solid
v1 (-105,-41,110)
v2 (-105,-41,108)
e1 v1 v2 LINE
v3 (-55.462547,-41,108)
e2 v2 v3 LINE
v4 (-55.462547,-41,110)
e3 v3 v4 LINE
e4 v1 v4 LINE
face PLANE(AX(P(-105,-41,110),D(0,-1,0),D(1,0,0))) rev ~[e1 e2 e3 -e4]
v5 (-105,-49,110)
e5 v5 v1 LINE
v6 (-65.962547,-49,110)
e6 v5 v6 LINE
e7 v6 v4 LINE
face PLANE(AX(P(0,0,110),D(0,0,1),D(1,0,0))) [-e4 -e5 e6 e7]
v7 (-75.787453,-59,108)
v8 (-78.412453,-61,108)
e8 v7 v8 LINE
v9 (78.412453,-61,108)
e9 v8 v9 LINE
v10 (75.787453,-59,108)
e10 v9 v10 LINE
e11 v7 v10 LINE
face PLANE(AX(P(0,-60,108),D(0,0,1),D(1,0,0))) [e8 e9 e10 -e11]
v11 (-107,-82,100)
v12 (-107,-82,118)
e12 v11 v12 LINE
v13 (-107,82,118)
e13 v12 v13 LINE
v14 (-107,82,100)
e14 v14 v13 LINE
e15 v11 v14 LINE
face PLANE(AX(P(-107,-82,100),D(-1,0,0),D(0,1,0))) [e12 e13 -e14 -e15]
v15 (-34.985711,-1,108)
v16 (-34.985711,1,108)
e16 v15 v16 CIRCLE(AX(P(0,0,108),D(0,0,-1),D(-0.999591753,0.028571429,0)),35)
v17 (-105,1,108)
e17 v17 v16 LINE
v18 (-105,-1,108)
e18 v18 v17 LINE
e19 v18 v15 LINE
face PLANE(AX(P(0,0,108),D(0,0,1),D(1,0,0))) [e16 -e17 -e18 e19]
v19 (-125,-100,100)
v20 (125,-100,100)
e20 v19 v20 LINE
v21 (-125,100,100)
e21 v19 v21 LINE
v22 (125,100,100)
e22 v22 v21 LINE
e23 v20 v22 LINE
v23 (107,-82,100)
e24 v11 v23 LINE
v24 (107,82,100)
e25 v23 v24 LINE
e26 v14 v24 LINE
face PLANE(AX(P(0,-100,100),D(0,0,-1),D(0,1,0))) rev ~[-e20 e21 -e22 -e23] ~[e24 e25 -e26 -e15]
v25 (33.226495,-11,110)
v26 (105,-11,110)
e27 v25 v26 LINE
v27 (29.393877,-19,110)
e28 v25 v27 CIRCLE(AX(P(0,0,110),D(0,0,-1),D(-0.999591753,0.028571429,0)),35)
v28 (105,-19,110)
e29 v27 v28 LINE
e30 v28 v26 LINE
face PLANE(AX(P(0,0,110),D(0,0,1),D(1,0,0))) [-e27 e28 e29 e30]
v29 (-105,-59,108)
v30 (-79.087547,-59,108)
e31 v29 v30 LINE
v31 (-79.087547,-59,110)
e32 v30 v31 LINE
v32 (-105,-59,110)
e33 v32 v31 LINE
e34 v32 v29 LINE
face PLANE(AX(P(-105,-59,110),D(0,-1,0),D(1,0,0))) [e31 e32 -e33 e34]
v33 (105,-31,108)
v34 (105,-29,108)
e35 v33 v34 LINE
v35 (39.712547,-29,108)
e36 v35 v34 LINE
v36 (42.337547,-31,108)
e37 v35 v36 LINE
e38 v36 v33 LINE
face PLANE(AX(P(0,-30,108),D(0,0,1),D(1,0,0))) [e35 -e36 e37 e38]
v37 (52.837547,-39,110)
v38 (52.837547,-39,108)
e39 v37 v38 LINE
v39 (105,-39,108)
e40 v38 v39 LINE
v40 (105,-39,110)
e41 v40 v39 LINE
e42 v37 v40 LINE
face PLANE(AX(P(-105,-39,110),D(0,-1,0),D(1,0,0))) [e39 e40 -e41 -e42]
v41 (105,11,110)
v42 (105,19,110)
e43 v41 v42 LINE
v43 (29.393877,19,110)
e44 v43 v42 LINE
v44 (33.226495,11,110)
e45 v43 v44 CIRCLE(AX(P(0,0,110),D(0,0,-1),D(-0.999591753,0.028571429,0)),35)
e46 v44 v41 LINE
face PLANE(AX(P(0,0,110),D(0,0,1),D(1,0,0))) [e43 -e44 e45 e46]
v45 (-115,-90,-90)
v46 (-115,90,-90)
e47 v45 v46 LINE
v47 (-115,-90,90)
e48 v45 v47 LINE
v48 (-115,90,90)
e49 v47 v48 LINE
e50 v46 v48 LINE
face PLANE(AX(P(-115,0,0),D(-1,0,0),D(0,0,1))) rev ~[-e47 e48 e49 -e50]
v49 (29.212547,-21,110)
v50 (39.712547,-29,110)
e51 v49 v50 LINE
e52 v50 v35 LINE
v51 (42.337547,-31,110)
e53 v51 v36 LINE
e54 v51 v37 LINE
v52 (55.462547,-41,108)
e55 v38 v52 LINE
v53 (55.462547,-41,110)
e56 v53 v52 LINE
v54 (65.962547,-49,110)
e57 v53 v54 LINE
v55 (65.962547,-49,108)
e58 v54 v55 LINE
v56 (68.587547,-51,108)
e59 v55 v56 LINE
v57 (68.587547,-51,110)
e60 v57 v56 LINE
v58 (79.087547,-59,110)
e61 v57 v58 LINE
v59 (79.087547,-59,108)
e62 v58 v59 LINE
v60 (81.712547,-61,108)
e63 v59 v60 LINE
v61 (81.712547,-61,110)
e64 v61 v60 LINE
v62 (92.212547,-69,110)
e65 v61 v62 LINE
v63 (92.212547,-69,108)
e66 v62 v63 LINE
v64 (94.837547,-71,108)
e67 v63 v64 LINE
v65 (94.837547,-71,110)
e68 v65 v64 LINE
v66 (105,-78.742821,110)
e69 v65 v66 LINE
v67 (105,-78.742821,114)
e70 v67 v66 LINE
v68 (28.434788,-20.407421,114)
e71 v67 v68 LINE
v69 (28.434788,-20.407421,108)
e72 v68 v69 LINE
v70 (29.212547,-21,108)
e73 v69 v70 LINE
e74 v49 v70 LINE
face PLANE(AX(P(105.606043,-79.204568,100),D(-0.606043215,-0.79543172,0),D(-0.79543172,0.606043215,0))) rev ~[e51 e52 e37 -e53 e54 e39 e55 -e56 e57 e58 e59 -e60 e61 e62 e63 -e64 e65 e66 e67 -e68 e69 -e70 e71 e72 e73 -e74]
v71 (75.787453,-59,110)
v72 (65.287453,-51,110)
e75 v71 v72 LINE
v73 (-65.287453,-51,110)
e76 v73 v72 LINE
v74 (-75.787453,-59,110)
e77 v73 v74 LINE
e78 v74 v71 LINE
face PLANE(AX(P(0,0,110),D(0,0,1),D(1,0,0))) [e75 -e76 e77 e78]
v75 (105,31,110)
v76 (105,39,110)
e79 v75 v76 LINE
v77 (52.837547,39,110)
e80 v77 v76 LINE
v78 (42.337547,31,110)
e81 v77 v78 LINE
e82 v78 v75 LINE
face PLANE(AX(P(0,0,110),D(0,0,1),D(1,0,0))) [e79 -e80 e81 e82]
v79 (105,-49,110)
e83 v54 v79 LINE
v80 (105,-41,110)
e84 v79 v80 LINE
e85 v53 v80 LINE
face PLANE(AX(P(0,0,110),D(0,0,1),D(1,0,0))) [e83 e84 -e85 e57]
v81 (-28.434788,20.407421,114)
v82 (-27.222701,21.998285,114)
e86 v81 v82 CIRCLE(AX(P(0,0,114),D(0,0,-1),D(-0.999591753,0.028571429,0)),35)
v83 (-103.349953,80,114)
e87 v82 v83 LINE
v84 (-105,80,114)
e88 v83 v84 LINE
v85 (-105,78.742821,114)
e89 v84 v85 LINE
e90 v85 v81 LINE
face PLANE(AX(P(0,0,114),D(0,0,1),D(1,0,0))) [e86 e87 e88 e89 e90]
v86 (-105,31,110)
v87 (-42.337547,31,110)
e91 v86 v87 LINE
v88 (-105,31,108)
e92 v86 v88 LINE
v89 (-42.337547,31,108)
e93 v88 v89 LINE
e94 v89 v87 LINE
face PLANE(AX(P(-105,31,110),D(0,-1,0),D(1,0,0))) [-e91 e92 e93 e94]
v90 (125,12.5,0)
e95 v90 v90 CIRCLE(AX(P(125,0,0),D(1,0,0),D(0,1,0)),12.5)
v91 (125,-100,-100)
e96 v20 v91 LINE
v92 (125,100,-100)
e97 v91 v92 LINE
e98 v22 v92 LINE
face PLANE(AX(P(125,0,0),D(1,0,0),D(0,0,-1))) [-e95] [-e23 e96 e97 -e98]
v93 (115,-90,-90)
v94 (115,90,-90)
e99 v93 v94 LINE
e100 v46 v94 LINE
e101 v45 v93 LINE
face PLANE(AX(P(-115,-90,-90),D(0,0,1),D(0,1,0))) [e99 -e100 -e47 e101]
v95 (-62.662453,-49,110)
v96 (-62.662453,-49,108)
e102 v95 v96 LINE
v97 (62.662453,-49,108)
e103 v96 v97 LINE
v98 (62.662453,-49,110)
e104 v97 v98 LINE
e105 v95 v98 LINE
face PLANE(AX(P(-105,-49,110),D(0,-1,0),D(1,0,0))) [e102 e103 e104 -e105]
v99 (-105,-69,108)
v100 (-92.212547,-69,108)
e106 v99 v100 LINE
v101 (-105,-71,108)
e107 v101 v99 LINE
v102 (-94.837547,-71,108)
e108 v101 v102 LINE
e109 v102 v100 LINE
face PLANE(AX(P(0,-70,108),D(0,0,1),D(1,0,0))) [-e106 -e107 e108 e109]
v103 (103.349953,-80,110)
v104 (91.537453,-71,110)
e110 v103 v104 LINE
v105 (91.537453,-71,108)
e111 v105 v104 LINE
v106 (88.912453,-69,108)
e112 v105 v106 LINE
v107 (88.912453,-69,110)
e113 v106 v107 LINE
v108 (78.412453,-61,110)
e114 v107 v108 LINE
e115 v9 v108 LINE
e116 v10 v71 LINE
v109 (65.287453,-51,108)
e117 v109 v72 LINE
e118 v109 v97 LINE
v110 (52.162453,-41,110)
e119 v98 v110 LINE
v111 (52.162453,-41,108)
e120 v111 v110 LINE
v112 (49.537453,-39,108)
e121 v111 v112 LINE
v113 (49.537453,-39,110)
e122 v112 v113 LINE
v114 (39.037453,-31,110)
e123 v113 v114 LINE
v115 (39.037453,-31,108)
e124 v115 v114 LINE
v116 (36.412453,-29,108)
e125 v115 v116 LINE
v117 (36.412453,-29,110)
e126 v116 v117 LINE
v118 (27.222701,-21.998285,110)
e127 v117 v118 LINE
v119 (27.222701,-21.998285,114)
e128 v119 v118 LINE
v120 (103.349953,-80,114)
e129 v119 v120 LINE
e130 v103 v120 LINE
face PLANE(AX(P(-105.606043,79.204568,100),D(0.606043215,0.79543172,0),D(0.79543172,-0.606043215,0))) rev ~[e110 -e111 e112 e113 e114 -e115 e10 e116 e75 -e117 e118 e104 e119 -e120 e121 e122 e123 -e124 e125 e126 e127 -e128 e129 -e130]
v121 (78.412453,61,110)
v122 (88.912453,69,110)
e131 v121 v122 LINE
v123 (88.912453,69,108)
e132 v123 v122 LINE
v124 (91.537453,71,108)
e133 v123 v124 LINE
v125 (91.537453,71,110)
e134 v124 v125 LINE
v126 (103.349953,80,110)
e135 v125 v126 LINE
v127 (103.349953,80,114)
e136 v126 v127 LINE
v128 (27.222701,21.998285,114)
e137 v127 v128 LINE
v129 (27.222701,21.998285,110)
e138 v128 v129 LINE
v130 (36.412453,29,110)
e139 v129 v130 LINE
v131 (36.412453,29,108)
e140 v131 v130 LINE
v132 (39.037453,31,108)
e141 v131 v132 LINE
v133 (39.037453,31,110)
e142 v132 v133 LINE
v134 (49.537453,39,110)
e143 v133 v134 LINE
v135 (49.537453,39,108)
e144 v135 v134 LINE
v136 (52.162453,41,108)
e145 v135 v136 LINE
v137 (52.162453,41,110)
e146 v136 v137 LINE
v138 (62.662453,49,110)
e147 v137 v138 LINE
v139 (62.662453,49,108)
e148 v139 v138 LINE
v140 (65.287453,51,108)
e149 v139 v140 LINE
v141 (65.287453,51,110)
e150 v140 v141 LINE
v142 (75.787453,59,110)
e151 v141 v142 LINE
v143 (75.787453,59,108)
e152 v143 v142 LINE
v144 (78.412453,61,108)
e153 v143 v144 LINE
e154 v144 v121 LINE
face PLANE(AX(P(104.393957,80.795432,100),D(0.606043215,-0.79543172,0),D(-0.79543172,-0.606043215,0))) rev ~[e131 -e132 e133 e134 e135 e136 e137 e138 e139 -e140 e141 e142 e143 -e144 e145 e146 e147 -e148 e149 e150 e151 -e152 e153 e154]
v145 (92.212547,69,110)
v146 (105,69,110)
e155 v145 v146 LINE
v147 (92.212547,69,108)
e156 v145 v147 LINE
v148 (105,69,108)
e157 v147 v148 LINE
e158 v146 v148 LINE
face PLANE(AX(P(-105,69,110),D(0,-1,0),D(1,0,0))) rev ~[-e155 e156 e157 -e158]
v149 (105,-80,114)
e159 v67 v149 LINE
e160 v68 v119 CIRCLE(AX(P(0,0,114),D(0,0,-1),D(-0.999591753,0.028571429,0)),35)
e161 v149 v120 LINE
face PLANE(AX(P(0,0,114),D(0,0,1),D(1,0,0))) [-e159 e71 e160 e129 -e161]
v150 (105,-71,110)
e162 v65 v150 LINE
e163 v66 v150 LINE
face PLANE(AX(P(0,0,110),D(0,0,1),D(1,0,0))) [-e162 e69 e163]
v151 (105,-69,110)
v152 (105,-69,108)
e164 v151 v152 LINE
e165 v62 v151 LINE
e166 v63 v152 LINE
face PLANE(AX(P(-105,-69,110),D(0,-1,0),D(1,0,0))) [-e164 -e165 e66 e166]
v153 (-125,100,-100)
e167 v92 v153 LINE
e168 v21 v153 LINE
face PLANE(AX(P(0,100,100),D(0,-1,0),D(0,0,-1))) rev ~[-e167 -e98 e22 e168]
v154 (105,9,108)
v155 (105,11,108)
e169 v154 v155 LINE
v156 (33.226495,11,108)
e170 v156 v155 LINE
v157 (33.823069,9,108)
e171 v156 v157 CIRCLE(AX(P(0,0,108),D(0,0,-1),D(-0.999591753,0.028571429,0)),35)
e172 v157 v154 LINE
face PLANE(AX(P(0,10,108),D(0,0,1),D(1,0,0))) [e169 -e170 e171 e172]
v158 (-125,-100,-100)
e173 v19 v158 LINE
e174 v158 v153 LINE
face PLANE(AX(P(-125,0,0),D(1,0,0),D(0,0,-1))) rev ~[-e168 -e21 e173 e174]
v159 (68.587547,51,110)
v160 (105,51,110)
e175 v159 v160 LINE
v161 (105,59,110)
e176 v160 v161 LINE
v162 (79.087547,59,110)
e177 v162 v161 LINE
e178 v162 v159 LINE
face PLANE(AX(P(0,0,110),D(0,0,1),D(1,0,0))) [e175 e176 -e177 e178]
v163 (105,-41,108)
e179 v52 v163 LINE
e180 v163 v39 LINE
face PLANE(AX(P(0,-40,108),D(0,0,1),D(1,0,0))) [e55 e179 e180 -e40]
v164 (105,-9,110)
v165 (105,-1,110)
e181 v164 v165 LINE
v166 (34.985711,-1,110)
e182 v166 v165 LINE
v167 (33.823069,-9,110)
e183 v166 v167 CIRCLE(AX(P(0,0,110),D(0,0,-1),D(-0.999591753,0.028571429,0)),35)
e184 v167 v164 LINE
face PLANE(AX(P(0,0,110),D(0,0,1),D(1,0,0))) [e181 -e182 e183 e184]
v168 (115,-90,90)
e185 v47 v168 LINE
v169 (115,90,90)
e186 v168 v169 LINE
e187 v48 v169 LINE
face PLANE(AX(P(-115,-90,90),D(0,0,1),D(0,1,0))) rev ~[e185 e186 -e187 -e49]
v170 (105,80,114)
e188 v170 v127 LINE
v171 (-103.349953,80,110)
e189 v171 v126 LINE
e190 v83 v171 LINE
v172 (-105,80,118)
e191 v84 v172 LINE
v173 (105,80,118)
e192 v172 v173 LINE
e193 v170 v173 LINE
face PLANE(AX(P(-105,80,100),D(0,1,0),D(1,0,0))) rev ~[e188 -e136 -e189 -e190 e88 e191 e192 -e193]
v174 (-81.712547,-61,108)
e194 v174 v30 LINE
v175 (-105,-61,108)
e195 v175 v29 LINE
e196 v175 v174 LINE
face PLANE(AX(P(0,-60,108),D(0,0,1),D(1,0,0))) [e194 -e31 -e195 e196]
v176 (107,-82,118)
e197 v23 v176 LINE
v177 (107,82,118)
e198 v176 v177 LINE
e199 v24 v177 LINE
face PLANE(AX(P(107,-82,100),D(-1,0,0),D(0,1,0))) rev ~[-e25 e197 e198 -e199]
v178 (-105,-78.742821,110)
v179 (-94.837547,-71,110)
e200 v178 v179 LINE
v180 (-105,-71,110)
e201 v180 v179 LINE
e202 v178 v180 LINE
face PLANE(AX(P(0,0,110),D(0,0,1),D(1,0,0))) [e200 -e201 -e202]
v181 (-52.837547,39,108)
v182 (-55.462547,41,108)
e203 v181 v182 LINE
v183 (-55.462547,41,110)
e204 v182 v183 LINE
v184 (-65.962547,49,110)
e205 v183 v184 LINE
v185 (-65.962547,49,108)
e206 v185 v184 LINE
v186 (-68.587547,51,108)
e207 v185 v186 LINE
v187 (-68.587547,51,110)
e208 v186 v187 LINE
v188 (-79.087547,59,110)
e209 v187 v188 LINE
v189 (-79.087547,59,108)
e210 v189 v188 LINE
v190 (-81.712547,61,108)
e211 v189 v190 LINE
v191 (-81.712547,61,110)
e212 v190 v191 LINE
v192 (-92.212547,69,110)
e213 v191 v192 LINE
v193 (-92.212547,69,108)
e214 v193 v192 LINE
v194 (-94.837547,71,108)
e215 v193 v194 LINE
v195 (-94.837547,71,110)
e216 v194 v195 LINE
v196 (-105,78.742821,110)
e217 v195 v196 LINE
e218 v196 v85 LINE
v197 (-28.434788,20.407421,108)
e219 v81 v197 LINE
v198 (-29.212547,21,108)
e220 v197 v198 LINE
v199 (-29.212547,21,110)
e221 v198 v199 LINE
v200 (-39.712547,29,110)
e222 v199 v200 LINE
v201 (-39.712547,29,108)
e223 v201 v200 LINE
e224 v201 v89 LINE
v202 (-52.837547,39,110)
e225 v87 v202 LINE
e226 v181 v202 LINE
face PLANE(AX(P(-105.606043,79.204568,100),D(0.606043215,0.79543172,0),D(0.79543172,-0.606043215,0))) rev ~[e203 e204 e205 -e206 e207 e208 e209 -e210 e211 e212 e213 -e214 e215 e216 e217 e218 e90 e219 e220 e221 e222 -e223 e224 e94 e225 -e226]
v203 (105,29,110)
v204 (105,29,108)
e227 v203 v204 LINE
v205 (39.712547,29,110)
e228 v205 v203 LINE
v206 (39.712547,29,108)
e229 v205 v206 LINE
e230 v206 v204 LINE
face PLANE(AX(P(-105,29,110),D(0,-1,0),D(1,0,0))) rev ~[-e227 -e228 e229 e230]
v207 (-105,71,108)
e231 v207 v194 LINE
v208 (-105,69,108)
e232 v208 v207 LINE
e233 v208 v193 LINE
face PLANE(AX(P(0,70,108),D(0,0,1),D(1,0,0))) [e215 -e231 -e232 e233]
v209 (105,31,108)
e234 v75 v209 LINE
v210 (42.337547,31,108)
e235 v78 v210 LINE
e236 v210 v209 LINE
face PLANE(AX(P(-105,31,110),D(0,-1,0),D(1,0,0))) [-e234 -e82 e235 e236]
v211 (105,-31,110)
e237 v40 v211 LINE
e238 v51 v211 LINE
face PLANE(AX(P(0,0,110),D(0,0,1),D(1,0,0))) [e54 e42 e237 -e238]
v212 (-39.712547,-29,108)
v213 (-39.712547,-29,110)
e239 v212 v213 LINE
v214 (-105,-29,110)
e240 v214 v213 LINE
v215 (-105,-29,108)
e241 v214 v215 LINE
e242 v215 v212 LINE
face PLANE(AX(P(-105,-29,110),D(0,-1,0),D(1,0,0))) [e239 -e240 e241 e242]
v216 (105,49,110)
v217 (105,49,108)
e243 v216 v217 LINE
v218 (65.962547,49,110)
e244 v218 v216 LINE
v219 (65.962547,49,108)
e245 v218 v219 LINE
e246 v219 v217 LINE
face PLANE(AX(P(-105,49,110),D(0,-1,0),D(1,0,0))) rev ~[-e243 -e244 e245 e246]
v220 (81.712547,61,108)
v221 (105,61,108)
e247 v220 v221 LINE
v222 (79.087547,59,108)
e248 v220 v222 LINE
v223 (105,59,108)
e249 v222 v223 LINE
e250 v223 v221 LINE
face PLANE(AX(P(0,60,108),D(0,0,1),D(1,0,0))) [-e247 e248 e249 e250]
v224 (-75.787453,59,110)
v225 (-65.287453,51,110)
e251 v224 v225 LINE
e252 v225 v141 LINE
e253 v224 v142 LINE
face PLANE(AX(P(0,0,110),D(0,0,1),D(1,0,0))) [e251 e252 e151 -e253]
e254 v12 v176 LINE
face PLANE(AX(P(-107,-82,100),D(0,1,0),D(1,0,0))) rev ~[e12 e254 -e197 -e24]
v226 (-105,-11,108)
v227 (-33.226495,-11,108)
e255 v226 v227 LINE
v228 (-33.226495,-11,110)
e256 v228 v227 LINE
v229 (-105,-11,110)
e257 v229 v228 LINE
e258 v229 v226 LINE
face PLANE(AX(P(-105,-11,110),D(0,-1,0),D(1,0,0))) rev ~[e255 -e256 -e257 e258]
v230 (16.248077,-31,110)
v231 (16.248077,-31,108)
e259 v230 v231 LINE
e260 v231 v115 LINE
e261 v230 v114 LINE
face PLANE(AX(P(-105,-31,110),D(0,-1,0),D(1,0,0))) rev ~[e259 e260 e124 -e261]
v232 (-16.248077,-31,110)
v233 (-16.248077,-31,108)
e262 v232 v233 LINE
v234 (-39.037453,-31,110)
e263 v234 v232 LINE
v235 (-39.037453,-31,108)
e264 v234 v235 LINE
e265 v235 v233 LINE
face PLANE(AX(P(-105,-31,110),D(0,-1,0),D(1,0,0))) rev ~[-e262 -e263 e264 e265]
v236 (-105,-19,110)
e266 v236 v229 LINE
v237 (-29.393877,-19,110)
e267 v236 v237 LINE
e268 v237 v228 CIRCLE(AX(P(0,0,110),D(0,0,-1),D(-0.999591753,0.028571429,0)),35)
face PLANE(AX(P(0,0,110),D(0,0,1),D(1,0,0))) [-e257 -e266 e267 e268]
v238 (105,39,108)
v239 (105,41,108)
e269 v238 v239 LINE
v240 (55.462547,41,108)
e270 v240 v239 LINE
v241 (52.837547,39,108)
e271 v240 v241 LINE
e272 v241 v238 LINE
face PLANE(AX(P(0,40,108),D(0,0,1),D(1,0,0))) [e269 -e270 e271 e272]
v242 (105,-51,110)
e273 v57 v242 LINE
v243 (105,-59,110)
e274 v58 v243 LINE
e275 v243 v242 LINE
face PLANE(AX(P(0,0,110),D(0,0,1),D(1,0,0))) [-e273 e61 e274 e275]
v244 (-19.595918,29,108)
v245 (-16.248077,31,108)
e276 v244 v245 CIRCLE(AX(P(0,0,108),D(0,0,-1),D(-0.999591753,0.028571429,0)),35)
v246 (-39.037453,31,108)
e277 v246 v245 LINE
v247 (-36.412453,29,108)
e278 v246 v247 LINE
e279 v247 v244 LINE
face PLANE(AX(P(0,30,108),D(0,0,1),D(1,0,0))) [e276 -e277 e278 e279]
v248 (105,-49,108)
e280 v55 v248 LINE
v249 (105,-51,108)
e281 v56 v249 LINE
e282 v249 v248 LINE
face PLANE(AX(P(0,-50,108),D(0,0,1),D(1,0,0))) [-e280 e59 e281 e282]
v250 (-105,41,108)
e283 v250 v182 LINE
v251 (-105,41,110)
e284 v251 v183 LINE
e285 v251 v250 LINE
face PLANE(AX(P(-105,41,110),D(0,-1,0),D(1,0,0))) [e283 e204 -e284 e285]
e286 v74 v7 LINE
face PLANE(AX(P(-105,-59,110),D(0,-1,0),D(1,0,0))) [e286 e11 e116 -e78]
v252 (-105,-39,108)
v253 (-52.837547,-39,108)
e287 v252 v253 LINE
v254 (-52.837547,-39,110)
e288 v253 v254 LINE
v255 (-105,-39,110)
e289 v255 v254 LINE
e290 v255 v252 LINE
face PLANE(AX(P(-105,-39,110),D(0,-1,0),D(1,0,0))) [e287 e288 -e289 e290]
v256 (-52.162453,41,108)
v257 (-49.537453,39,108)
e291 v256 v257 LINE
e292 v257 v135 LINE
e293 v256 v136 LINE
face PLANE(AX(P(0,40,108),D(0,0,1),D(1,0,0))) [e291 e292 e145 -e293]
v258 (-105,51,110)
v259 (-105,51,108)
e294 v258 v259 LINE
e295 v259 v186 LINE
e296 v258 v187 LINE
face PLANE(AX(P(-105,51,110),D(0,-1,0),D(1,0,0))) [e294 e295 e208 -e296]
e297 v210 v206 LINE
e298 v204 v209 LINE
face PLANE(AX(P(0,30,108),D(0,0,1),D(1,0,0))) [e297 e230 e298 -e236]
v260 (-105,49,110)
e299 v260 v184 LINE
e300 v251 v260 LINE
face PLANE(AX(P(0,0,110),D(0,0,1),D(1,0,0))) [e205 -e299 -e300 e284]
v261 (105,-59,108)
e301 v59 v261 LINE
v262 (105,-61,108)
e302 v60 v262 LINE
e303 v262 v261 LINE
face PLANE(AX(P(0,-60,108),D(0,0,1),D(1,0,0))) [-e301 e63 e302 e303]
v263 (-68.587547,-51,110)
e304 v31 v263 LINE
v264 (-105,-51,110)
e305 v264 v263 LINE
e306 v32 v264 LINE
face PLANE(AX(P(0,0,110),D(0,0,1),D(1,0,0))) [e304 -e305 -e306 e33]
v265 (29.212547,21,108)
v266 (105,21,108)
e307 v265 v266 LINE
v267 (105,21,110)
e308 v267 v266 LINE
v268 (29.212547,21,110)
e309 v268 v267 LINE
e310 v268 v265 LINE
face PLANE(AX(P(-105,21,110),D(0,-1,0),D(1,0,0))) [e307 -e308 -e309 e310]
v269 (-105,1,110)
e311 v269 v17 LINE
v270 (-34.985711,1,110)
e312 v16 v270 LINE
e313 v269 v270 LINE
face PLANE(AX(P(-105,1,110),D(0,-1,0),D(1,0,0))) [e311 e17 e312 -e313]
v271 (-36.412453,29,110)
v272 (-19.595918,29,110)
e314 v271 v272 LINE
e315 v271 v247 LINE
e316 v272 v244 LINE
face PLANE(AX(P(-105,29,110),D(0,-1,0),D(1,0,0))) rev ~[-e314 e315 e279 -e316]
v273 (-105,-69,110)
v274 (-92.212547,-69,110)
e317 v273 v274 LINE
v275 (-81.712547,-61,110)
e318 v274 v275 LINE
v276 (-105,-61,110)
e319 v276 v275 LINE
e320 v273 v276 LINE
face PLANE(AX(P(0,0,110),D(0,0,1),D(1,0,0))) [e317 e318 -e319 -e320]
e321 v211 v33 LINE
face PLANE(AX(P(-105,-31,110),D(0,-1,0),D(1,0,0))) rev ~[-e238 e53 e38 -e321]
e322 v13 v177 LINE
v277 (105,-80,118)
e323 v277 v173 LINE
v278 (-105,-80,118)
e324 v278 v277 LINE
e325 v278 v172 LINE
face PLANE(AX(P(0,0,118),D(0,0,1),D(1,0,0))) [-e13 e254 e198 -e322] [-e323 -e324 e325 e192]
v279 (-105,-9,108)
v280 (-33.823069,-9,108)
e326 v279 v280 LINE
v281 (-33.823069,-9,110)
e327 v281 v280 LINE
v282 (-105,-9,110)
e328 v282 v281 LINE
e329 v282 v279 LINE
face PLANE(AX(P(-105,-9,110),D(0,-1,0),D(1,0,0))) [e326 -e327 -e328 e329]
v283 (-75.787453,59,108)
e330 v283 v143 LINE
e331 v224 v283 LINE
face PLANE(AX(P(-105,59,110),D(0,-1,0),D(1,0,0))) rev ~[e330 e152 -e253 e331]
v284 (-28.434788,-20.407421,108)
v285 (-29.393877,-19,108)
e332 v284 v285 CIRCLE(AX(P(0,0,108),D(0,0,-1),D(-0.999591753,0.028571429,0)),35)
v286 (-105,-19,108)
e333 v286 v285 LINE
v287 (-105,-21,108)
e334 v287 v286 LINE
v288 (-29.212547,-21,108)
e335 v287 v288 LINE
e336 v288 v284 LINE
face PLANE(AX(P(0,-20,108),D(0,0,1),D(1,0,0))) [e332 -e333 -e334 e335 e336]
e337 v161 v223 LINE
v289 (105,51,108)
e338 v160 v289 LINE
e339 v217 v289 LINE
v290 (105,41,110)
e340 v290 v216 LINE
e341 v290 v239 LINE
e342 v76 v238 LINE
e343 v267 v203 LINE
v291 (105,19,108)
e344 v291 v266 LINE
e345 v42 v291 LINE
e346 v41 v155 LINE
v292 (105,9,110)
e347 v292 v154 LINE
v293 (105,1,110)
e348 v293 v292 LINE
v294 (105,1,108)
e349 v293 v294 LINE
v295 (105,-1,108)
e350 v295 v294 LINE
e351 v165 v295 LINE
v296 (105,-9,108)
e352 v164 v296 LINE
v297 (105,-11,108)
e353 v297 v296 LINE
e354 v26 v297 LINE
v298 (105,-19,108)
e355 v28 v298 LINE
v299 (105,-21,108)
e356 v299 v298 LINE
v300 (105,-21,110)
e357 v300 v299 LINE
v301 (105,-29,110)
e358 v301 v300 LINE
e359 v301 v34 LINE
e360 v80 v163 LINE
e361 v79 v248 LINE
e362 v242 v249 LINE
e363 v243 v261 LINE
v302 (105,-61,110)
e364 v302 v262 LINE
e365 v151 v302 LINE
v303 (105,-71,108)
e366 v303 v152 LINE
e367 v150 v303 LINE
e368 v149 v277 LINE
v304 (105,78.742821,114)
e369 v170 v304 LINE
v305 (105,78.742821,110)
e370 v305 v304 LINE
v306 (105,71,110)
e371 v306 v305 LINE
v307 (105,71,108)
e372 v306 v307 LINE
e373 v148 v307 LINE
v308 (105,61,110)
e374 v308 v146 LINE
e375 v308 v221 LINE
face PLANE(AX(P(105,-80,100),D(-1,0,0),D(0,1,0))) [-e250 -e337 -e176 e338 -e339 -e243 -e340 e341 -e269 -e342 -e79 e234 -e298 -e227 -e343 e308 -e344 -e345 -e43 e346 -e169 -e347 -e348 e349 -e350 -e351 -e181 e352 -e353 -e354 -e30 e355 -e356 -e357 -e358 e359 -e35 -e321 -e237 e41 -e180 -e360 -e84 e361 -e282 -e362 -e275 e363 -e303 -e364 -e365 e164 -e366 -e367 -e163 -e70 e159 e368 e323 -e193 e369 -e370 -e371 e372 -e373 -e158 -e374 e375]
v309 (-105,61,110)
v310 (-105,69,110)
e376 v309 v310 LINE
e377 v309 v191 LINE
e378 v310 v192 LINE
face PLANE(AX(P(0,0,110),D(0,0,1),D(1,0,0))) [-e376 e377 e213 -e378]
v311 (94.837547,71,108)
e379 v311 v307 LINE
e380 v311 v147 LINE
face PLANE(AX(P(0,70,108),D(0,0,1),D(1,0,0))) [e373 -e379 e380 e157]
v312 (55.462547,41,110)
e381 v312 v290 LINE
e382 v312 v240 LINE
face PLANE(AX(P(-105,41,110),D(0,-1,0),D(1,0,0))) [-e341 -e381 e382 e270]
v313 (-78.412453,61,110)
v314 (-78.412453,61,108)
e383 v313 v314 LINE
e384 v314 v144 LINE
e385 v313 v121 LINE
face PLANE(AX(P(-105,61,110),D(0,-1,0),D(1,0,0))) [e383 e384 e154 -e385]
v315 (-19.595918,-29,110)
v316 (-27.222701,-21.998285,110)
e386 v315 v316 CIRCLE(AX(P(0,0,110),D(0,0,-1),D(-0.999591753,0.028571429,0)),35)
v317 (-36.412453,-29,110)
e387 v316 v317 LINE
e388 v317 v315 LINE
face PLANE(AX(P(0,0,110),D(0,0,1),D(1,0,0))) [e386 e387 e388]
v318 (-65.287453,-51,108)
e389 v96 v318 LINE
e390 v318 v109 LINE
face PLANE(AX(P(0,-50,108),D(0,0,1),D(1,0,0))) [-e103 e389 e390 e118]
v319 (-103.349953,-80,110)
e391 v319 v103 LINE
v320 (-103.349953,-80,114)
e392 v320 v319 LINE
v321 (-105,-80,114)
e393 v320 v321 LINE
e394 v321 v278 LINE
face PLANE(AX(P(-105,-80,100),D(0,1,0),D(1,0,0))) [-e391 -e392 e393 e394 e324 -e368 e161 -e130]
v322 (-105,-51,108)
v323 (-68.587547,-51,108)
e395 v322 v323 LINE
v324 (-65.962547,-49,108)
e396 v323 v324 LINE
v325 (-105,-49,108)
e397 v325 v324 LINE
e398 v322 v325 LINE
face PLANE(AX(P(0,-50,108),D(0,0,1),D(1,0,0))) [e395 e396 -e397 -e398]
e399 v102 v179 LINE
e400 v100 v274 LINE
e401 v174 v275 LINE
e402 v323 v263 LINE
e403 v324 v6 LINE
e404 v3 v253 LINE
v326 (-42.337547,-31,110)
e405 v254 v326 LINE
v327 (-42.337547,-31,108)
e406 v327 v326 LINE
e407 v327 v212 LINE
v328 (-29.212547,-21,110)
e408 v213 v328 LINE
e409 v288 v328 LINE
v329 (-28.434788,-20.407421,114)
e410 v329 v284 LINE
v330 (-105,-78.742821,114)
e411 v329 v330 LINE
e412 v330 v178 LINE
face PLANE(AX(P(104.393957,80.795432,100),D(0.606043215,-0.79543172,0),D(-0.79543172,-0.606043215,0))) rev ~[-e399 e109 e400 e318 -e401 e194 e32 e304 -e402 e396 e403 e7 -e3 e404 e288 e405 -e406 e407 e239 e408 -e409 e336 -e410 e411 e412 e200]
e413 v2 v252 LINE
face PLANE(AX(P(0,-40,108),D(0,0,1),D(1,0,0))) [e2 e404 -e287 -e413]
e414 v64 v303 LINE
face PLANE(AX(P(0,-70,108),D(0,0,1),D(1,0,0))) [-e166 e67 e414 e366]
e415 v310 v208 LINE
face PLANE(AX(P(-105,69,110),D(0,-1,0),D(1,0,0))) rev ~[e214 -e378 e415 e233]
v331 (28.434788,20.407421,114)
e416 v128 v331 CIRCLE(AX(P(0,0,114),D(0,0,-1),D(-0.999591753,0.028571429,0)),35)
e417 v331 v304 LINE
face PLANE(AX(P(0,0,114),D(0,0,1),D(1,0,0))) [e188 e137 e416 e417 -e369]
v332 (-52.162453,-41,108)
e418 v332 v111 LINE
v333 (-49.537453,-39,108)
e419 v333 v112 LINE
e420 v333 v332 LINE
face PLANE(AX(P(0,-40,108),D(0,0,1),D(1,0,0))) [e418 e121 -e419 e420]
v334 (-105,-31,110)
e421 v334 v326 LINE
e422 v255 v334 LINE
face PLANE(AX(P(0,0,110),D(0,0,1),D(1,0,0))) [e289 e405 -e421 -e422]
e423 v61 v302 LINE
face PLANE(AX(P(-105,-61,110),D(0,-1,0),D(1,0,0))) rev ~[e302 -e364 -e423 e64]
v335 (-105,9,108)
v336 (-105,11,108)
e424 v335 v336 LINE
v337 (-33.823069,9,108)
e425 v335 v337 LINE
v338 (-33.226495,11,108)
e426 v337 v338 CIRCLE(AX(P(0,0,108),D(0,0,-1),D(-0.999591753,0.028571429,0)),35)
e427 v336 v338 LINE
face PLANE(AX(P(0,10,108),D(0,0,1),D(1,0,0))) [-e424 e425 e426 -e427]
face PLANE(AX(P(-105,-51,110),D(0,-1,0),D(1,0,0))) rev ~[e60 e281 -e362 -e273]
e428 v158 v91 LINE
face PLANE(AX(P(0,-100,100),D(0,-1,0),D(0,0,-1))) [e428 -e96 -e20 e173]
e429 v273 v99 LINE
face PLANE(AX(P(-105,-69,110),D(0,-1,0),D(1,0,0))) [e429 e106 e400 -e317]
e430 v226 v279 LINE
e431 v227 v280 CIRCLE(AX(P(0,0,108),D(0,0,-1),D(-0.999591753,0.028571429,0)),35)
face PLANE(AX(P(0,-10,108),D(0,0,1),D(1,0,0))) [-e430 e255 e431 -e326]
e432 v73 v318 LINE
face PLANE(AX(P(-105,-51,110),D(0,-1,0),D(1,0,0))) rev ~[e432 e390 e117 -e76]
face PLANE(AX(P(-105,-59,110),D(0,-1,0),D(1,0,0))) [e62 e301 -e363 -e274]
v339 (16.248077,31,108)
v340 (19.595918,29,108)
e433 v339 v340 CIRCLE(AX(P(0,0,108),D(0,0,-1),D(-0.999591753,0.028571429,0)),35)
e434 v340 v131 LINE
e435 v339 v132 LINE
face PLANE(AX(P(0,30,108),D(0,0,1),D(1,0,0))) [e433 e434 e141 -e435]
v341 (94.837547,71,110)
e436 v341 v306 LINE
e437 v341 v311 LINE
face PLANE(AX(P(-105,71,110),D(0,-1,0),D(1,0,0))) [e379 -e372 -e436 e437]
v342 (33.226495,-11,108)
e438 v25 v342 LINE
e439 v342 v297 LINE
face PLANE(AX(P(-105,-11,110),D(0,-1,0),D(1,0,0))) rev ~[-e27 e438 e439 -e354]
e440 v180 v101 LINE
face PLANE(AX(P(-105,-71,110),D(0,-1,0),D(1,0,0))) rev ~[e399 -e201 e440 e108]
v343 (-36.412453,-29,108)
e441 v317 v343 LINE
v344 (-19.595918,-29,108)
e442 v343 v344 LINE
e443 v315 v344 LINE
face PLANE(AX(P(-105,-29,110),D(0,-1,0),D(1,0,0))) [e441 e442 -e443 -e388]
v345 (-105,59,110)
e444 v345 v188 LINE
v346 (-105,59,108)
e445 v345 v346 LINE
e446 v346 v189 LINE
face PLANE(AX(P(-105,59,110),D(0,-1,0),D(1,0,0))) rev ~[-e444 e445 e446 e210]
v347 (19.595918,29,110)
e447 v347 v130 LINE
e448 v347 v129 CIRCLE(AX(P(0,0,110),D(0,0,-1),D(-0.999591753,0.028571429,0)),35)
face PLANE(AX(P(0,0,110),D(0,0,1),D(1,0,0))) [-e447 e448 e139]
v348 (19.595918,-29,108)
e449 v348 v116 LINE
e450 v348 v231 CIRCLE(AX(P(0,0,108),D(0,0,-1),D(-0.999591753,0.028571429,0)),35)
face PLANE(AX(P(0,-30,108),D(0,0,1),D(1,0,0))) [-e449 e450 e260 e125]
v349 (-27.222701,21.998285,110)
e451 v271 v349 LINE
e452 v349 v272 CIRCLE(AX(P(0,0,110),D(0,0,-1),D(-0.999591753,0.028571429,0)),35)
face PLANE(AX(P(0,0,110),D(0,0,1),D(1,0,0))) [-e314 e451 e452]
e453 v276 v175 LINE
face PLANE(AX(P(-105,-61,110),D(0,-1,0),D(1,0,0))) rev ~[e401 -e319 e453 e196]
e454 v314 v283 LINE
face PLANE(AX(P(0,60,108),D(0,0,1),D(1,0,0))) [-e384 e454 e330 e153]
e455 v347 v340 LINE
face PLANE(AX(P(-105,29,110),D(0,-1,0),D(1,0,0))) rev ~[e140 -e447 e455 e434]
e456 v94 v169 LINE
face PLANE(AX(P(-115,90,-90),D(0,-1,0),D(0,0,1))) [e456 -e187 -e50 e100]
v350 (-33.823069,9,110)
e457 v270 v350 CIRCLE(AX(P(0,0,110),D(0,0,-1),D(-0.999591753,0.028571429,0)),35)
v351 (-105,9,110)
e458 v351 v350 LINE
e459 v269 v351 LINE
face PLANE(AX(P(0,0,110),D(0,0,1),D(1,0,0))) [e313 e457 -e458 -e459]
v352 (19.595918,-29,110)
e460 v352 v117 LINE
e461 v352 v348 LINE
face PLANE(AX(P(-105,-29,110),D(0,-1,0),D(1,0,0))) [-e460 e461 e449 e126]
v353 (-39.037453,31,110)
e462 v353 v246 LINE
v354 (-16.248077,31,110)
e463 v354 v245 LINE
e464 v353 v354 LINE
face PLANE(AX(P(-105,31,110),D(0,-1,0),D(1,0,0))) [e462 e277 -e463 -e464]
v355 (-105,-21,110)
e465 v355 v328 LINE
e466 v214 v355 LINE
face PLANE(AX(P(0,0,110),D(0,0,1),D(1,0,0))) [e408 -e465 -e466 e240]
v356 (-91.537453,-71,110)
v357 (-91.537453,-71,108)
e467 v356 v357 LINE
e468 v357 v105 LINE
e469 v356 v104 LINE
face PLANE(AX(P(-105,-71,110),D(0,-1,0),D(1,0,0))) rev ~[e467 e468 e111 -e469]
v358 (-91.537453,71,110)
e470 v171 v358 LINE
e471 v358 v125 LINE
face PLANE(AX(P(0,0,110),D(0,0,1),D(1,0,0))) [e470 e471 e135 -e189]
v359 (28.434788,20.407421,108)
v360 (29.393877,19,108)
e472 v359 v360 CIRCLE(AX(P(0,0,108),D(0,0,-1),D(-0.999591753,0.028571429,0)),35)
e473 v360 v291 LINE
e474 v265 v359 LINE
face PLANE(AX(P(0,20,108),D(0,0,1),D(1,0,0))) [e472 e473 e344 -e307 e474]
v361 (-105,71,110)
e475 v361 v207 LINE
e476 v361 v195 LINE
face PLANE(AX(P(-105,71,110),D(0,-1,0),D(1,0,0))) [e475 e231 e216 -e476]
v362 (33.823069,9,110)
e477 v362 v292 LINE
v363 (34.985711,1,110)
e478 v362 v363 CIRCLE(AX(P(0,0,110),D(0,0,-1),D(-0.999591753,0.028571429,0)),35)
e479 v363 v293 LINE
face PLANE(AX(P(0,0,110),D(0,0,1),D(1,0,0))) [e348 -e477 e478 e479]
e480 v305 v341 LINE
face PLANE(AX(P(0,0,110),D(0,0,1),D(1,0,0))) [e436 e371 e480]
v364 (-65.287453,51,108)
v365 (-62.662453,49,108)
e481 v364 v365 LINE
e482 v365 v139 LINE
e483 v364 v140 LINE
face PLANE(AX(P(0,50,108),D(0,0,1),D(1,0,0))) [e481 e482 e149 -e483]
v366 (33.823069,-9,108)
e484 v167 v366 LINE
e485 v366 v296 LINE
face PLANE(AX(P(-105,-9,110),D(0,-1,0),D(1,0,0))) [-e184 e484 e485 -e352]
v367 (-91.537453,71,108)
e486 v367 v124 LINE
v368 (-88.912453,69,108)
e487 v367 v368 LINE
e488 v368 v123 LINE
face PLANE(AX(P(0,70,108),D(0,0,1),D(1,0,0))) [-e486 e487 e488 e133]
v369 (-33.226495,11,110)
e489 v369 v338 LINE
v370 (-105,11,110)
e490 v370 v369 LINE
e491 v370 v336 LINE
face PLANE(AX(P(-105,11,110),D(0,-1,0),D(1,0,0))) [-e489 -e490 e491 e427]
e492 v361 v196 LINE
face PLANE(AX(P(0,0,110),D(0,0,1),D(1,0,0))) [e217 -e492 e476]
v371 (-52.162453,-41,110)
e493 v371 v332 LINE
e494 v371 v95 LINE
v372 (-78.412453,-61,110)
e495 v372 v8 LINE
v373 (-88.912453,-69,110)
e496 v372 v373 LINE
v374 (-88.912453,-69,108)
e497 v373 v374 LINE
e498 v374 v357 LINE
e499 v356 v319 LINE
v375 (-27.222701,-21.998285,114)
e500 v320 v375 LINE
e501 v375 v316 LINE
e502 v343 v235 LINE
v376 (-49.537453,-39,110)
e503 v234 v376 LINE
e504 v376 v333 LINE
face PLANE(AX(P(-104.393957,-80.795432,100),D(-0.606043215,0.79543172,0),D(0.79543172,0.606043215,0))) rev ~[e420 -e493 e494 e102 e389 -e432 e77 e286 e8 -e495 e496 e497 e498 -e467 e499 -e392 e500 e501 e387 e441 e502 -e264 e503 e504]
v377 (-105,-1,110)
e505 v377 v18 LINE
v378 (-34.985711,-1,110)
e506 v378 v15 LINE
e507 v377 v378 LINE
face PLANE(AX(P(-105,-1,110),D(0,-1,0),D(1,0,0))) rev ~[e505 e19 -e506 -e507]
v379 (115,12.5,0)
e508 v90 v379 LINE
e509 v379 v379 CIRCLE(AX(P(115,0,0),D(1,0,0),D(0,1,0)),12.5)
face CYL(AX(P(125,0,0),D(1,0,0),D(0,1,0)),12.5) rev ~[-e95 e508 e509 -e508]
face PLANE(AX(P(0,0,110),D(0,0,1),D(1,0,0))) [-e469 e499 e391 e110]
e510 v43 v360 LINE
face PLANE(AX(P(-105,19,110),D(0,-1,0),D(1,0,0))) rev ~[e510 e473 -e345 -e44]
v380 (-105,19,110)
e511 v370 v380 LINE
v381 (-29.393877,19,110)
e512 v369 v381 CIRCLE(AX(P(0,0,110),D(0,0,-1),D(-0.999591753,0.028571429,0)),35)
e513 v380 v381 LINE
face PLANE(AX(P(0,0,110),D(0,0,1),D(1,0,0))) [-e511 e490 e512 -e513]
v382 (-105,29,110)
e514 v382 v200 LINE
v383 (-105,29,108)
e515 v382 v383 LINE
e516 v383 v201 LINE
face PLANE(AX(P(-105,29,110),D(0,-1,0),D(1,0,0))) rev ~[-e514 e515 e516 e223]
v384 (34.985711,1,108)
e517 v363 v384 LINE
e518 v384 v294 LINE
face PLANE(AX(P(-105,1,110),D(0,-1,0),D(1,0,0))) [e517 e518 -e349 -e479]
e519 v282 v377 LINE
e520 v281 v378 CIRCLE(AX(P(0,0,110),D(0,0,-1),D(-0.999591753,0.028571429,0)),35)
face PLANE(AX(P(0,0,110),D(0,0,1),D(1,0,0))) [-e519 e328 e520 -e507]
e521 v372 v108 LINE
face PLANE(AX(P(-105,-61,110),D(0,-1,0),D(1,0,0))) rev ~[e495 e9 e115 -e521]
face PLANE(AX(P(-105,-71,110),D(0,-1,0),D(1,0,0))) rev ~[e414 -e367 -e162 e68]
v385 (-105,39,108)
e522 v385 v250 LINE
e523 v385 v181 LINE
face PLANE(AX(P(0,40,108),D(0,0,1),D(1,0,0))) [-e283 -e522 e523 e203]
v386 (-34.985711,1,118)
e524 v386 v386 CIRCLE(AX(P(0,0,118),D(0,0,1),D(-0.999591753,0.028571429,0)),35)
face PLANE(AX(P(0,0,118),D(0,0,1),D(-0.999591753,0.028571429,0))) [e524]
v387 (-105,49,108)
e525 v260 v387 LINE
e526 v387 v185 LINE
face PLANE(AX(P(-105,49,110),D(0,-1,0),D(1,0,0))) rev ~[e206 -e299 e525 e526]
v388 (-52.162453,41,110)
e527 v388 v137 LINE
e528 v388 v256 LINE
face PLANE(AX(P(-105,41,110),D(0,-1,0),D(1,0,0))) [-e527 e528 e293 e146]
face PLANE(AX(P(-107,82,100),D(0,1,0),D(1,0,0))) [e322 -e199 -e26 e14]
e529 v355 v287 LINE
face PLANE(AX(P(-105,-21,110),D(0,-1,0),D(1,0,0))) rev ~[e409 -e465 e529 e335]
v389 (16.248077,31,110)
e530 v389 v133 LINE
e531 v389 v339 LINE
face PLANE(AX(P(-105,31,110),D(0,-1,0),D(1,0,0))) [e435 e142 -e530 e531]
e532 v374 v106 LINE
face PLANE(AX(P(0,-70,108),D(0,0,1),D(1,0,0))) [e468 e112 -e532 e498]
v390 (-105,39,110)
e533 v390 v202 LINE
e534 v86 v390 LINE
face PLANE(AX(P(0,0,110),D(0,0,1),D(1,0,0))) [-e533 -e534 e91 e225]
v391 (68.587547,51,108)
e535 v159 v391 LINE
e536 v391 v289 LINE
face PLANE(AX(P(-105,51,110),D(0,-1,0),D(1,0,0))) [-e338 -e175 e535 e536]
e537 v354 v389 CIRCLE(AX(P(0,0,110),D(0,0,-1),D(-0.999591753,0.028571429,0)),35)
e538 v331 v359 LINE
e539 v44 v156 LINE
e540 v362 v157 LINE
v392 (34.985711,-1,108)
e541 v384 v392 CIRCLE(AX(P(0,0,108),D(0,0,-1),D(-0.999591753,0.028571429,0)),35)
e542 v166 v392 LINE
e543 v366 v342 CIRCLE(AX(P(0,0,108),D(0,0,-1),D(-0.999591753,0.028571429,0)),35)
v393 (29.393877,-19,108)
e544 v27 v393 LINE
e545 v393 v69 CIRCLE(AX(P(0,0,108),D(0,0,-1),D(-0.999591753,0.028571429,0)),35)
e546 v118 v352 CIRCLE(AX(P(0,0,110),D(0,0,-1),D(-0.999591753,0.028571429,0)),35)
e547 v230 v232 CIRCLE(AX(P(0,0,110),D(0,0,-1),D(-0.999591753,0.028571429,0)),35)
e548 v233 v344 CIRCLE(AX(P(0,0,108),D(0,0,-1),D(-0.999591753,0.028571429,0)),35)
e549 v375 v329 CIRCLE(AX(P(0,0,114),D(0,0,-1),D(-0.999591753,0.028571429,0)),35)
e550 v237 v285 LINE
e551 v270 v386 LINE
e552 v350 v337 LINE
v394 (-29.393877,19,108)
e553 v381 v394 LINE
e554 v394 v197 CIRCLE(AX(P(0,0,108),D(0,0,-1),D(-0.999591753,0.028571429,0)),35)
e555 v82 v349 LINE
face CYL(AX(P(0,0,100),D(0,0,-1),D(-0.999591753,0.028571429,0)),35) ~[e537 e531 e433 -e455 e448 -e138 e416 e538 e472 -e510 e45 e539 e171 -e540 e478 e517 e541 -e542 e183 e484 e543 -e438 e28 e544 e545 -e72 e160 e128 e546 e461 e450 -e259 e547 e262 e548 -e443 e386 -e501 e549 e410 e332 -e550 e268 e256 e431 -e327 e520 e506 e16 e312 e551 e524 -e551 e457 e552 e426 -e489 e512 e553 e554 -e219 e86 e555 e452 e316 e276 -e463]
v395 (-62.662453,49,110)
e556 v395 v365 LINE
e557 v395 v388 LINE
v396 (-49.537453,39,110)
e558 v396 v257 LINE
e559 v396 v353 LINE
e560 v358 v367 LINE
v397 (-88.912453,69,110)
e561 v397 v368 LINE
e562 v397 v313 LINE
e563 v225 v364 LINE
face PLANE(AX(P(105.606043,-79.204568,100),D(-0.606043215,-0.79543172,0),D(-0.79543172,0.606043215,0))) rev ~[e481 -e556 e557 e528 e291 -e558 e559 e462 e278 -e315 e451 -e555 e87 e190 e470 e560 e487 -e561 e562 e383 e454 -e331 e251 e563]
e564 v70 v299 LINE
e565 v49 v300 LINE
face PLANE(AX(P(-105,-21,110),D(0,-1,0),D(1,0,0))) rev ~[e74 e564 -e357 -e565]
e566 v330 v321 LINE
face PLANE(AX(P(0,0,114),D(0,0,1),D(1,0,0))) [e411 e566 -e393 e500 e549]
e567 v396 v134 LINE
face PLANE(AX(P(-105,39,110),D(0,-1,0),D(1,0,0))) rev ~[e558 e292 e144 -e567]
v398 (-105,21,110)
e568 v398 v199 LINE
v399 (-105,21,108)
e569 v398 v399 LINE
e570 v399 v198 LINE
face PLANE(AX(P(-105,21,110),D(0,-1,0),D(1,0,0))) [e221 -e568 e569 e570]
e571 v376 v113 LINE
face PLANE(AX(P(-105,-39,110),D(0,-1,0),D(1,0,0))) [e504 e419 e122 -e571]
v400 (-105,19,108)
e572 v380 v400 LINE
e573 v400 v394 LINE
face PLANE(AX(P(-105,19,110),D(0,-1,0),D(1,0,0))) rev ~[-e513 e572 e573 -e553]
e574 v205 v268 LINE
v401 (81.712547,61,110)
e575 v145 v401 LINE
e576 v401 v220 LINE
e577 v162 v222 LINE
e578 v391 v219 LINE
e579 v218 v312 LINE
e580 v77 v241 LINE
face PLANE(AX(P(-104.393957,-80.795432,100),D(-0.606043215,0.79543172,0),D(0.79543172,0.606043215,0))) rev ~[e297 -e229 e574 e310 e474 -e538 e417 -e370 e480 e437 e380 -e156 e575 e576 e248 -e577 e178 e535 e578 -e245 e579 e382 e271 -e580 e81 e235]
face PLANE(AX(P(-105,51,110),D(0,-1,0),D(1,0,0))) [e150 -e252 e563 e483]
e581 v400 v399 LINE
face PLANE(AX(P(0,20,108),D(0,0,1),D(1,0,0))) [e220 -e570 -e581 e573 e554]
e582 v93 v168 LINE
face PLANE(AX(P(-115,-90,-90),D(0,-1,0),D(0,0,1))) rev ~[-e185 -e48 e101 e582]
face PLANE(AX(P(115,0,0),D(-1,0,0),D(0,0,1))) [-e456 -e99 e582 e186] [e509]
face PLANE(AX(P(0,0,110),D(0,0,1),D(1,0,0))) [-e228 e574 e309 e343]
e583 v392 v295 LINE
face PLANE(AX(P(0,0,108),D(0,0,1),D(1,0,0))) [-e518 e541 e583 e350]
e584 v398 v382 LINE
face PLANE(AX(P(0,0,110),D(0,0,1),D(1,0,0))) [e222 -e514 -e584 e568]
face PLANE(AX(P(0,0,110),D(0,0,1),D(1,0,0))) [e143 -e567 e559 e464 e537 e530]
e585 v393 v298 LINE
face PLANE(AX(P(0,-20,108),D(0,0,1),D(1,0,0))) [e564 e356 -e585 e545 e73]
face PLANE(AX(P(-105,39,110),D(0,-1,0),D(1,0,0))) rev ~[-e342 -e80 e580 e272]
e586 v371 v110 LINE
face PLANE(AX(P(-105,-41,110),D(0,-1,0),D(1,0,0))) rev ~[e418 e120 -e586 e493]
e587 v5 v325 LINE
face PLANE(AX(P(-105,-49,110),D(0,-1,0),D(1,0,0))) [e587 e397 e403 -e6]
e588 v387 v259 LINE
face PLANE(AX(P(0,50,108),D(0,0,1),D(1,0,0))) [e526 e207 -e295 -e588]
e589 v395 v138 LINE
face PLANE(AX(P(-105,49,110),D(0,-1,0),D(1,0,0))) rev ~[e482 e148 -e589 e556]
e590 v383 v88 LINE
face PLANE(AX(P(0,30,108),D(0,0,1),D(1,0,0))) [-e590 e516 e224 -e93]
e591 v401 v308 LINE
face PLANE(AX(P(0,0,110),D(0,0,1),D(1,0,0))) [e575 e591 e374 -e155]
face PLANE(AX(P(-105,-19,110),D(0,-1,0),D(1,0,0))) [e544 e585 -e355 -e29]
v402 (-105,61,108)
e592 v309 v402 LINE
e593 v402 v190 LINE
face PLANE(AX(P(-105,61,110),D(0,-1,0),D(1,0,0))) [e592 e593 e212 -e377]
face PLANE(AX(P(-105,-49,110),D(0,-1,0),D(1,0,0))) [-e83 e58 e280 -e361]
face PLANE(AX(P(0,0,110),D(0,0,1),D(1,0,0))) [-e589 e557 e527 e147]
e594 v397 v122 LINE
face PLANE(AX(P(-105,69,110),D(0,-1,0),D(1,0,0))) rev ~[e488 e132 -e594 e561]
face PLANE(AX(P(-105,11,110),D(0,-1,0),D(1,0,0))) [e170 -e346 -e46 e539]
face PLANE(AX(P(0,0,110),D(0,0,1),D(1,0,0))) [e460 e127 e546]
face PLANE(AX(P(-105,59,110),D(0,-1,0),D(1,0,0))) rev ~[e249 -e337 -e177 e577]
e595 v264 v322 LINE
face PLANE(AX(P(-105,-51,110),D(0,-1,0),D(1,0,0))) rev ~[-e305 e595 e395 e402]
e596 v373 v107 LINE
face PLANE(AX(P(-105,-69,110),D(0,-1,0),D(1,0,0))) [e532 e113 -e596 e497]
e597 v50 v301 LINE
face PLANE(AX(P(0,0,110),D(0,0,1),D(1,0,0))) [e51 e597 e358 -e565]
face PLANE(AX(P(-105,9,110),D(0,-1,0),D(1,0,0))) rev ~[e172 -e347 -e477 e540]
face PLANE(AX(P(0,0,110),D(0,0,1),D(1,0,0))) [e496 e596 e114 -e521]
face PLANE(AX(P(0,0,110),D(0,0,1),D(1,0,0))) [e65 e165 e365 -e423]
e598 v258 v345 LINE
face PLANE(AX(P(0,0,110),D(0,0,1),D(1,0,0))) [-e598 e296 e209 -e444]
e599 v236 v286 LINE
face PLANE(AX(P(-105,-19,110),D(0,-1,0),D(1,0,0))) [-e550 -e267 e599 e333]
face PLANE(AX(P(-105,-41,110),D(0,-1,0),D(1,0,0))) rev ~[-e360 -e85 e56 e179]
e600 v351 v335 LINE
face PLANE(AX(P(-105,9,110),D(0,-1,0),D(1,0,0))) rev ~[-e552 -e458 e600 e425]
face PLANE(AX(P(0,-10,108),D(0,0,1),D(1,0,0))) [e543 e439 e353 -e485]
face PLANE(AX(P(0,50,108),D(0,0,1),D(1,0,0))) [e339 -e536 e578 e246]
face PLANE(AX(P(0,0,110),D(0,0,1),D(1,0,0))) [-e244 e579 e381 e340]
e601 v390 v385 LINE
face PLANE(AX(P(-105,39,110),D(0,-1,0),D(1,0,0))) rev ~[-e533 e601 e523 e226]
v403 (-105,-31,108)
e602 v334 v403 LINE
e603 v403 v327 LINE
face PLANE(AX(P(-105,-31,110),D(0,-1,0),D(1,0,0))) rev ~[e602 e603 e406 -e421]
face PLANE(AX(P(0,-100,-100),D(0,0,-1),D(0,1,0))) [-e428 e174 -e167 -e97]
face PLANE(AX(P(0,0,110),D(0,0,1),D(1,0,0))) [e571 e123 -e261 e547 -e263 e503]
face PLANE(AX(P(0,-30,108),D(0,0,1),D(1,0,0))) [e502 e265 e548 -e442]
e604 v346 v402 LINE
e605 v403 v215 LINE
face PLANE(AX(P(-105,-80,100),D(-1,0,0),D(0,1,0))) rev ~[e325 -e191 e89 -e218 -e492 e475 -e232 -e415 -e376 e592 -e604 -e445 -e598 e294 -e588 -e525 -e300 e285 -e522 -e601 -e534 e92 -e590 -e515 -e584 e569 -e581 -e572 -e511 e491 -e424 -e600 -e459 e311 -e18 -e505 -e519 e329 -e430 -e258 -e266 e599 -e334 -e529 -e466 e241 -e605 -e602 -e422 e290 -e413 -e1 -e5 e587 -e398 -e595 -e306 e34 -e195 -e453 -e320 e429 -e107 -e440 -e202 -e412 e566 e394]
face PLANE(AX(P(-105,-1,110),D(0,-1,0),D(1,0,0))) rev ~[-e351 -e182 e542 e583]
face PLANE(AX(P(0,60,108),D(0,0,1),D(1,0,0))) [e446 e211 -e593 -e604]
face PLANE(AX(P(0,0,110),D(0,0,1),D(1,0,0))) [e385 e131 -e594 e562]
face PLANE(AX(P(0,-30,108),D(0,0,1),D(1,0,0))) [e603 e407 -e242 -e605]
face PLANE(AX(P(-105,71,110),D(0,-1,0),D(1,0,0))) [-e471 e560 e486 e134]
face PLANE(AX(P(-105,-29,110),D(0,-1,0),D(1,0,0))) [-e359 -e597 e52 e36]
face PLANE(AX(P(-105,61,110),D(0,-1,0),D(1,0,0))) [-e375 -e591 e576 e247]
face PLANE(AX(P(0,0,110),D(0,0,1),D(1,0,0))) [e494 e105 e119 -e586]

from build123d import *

# Parameters (mm, degrees)
SKETCH1_W               = 200
SKETCH1_H               = 200
BOSS_EXTRUDE1_DEPTH     = 125
SKETCH2_W               = 210
SKETCH2_H               = 160
BOSS_EXTRUDE2_DEPTH     = 10
SKETCH8_W               = 210
SKETCH8_H               = 2
CUT_EXTRUDE_THIN5_DEPTH = 2
LPATTERN1_COUNT         = 8
LPATTERN1_PITCH         = 10
LPATTERN1_COL_COUNT     = 8
LPATTERN1_COL_PITCH     = 10
SKETCH11_R              = 35
BOSS_EXTRUDE9_DEPTH     = 18
EXTRUDE_THIN2_DEPTH     = 14
EXTRUDE_THIN3_DEPTH     = 14
SKETCH14_W              = 214
SKETCH14_H              = 164
SKETCH14_W_2            = 210
SKETCH14_H_2            = 160
BOSS_EXTRUDE10_DEPTH    = 18
CUT_EXTRUDE1_START      = -10
SKETCH15_W              = 180
SKETCH15_H              = 180
CUT_EXTRUDE1_DEPTH      = 230
SKETCH16_R              = 12.5
CUT_EXTRUDE2_DEPTH      = 83


with BuildPart() as part:
    # Sketch1 → Boss-Extrude1 (new, symmetric)
    with BuildSketch(Plane(origin=(0, 0, 0), x_dir=(0, 0, -1), z_dir=(1, 0, 0))):
        Rectangle(SKETCH1_W, SKETCH1_H)
    extrude(amount=BOSS_EXTRUDE1_DEPTH, both=True)

    # Sketch2 → Boss-Extrude2 (add)
    with BuildSketch(Plane.XY.offset(100)):
        Rectangle(SKETCH2_W, SKETCH2_H)
    extrude(amount=BOSS_EXTRUDE2_DEPTH)

    # Sketch8 → Cut-Extrude-Thin5 (cut)
    with BuildSketch(Plane.XY.offset(110)):
        Rectangle(SKETCH8_W, SKETCH8_H)
    cut_extrude_thin5 = extrude(amount=-CUT_EXTRUDE_THIN5_DEPTH, mode=Mode.SUBTRACT)

    # LPattern1: Cut-Extrude-Thin5 ×8
    with Locations(*[(0, i * LPATTERN1_PITCH, 0) for i in range(1, LPATTERN1_COUNT)]):
        add(cut_extrude_thin5, mode=Mode.SUBTRACT)

    # LPattern1 col: Cut-Extrude-Thin5 ×8
    with Locations(*[(0, -i * LPATTERN1_COL_PITCH, 0) for i in range(1, LPATTERN1_COL_COUNT)]):
        add(cut_extrude_thin5, mode=Mode.SUBTRACT)

    # Sketch11 → Boss-Extrude9 (add)
    with BuildSketch(Plane.XY.offset(100)):
        with Locations(Location((0, 0, 0), (0, 0, 178.362754922))):
            Circle(SKETCH11_R)
    extrude(amount=BOSS_EXTRUDE9_DEPTH)

    # Sketch12 → Extrude-Thin2 (add)
    with BuildSketch(Plane.XY.offset(100)):
        Polygon((-105.606043215, 79.20456828), (104.393956785, -80.79543172), (105.606043215, -79.20456828), (-104.393956785, 80.79543172), align=None)
    extrude(amount=EXTRUDE_THIN2_DEPTH)

    # Sketch13 → Extrude-Thin3 (add)
    with BuildSketch(Plane.XY.offset(100)):
        Polygon((104.393956785, 80.79543172), (-105.606043215, -79.20456828), (-104.393956785, -80.79543172), (105.606043215, 79.20456828), align=None)
    extrude(amount=EXTRUDE_THIN3_DEPTH)

    # Sketch14 → Boss-Extrude10 (add)
    with BuildSketch(Plane.XY.offset(100)):
        Rectangle(SKETCH14_W, SKETCH14_H)
        Rectangle(SKETCH14_W_2, SKETCH14_H_2, mode=Mode.SUBTRACT)
    extrude(amount=BOSS_EXTRUDE10_DEPTH)

    # Sketch15 → Cut-Extrude1 (cut)
    with BuildSketch(Plane.ZY.offset(125).offset(CUT_EXTRUDE1_START)):
        Rectangle(SKETCH15_W, SKETCH15_H)
    extrude(amount=-CUT_EXTRUDE1_DEPTH, mode=Mode.SUBTRACT)

    # Sketch16 → Cut-Extrude2 (cut)
    with BuildSketch(Plane(origin=(125, 0, 0), x_dir=(0, 0, -1), z_dir=(1, 0, 0))):
        with Locations(Location((0, 0, 0), (0, 0, 90))):
            Circle(SKETCH16_R)
    extrude(amount=-CUT_EXTRUDE2_DEPTH, mode=Mode.SUBTRACT)


solid = part.part
